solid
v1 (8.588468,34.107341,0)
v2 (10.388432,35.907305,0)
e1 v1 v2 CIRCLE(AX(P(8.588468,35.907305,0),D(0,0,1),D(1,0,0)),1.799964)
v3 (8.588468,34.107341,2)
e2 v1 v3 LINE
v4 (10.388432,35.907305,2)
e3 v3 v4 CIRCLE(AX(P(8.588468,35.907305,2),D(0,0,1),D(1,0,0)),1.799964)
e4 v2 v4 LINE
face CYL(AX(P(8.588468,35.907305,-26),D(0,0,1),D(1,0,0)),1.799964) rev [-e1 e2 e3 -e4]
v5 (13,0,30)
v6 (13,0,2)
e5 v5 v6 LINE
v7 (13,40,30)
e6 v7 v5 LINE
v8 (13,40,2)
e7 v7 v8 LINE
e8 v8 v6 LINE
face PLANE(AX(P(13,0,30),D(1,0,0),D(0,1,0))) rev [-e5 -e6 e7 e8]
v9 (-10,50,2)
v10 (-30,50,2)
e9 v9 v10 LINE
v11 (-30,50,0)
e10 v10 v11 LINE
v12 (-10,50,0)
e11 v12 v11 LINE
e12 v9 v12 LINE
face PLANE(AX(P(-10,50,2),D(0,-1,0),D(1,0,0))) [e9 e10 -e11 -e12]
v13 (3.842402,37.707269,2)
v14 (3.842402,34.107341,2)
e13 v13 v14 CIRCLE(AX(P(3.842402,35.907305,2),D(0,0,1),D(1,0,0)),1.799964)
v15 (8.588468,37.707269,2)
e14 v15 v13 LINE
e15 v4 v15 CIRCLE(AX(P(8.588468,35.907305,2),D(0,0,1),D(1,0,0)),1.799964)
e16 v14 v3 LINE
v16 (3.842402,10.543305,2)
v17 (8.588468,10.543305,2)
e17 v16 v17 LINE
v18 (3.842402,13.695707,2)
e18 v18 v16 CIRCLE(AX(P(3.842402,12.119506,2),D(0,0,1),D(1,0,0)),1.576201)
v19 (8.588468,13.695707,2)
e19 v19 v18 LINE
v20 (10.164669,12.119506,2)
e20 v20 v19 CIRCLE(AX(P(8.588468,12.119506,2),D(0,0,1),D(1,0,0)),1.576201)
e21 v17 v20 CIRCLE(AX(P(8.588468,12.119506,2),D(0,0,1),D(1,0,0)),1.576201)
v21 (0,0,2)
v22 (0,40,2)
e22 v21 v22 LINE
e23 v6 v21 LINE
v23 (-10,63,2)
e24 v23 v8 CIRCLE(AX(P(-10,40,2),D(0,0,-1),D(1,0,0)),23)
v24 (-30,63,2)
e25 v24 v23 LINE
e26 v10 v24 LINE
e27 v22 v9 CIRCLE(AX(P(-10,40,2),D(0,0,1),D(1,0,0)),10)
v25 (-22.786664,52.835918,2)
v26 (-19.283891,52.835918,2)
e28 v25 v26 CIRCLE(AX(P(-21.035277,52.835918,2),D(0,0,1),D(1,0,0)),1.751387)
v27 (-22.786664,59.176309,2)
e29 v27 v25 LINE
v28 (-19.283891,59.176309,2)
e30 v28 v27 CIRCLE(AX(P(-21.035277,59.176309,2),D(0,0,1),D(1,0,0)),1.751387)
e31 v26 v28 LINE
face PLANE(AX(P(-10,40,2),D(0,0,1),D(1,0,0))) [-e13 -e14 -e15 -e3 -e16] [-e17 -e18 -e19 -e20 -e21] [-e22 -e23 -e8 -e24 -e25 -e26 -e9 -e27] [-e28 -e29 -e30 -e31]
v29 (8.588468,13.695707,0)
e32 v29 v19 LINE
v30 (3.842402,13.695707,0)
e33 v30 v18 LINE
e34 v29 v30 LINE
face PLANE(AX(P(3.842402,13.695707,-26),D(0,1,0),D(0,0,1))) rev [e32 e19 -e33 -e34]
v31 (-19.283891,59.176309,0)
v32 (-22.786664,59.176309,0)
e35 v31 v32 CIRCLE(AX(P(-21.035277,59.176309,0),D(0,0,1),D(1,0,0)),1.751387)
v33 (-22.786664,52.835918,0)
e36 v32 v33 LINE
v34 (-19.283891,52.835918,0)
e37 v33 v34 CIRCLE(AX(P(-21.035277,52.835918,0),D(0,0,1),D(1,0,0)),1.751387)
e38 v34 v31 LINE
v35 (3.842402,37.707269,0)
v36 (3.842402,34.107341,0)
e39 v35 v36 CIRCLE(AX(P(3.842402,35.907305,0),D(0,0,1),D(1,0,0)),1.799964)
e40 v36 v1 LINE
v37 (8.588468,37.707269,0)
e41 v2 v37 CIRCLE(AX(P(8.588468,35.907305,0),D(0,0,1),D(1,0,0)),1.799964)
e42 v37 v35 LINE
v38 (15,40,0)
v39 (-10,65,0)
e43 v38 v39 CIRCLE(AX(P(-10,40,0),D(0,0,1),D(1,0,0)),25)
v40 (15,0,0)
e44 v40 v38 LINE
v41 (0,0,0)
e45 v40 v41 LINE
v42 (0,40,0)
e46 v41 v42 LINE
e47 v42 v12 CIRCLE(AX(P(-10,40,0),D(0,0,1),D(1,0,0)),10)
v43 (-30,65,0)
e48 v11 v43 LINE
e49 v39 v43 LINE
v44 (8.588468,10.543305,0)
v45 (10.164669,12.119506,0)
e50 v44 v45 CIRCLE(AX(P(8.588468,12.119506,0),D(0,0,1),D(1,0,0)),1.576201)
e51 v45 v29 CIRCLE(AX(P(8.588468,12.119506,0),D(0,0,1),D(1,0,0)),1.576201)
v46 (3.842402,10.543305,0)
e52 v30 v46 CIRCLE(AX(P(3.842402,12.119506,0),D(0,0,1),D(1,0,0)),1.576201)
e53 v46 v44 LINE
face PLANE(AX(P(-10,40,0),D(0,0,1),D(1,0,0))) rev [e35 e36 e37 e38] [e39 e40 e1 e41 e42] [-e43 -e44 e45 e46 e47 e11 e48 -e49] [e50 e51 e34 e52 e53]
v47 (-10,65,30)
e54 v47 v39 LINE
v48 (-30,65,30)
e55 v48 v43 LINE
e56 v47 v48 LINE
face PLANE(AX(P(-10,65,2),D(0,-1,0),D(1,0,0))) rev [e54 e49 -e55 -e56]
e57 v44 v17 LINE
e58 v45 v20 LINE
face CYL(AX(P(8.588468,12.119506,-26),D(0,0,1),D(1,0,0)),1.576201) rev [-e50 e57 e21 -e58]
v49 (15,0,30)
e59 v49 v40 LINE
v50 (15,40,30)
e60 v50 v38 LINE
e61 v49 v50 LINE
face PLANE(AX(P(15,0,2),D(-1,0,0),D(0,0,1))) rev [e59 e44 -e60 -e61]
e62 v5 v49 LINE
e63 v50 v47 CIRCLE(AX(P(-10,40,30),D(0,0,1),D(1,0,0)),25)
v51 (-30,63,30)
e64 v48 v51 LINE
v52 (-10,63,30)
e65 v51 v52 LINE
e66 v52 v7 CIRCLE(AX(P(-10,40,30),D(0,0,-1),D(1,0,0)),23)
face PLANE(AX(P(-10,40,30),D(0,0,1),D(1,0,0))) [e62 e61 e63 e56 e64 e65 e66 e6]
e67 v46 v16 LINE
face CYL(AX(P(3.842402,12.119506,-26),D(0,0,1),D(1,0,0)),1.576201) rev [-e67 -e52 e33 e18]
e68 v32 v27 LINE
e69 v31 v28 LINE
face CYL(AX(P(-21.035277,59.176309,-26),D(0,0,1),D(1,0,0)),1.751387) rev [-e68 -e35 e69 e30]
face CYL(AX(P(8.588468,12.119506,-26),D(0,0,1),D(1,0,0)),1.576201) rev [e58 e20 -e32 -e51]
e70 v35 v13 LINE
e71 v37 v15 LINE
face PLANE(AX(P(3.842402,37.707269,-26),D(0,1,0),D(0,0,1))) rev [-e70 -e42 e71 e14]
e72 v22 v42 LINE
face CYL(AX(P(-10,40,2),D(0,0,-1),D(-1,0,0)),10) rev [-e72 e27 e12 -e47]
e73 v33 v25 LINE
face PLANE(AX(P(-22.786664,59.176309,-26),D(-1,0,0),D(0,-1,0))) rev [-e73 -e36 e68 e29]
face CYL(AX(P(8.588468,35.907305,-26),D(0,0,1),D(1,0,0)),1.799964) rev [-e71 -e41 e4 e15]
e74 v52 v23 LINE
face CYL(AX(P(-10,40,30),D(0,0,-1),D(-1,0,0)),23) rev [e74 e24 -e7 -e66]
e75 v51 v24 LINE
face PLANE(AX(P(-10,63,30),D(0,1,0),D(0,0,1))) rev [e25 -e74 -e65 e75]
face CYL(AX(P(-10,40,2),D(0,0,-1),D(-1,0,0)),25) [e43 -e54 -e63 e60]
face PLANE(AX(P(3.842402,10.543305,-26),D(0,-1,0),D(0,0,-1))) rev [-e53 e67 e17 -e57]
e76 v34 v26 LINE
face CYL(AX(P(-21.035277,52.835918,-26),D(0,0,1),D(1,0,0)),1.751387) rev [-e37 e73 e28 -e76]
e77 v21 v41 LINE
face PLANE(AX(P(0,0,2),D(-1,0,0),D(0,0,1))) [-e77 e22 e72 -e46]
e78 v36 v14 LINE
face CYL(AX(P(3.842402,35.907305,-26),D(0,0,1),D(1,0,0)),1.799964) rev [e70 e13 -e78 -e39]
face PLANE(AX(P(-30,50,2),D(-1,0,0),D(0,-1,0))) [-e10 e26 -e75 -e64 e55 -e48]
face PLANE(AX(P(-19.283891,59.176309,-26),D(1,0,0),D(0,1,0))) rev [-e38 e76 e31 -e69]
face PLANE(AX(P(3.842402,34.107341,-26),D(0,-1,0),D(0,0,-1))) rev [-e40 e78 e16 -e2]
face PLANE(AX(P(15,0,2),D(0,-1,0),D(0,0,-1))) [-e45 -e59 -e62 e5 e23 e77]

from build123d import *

# Parameters (mm, degrees)
EXTRUDE_THIN1_DEPTH = 2
BOSS_EXTRUDE1_DEPTH = 28
CUT_EXTRUDE1_DEPTH  = 28


with BuildPart() as part:
    # Sketch1 → Extrude-Thin1 (new body)
    with BuildSketch(Plane.XY):
        with BuildLine():
            Line((0, 0), (0, 40))
            ThreePointArc((0, 40), (-2.928932188, 47.071067812), (-10, 50))
            Line((-10, 50), (-30, 50))
            Line((-30, 50), (-30, 65))
            Line((-30, 65), (-10, 65))
            ThreePointArc((-10, 65), (7.67766953, 57.67766953), (15, 40))
            Line((15, 40), (15, 0))
            Line((15, 0), (0, 0))
        make_face()
    extrude(amount=EXTRUDE_THIN1_DEPTH)

    # Sketch2 → Boss-Extrude1 (add)
    with BuildSketch(Plane.XY.offset(2)):
        with BuildLine():
            Line((13, 0), (13, 40))
            ThreePointArc((13, 40), (6.263455967, 56.263455967), (-10, 63))
            Line((-10, 63), (-30, 63))
            Line((-30, 63), (-30, 65))
            Line((-30, 65), (-10, 65))
            ThreePointArc((-10, 65), (7.67766953, 57.67766953), (15, 40))
            Line((15, 40), (15, 0))
            Line((15, 0), (13, 0))
        make_face()
    extrude(amount=BOSS_EXTRUDE1_DEPTH)

    # Sketch3 → Cut-Extrude1 (cut)
    with BuildSketch(Plane.XY.offset(2)):
        with BuildLine():
            Line((-19.283890524, 59.176308794), (-19.283890524, 52.835918308))
            ThreePointArc((-19.283890524, 52.835918308), (-21.035277496, 51.084531336), (-22.786664469, 52.835918308))
            Line((-22.786664469, 52.835918308), (-22.786664469, 59.176308794))
            ThreePointArc((-22.786664469, 59.176308794), (-21.035277496, 60.927695767), (-19.283890524, 59.176308794))
        make_face()
        with BuildLine():
            Line((3.842402099, 13.695706596), (8.588468352, 13.695706596))
            ThreePointArc((8.588468352, 13.695706596), (10.164668971, 12.119505978), (8.588468352, 10.543305359))
            Line((8.588468352, 10.543305359), (3.842402099, 10.543305359))
            ThreePointArc((3.842402099, 10.543305359), (2.26620148, 12.119505978), (3.842402099, 13.695706596))
        make_face()
        with BuildLine():
            Line((3.842402099, 37.707268764), (8.588468352, 37.707268764))
            ThreePointArc((8.588468352, 37.707268764), (10.388432438, 35.907304678), (8.588468352, 34.107340593))
            Line((8.588468352, 34.107340593), (3.842402099, 34.107340593))
            ThreePointArc((3.842402099, 34.107340593), (2.042438013, 35.907304678), (3.842402099, 37.707268764))
        make_face()
    extrude(amount=-CUT_EXTRUDE1_DEPTH, mode=Mode.SUBTRACT)


solid = part.part
